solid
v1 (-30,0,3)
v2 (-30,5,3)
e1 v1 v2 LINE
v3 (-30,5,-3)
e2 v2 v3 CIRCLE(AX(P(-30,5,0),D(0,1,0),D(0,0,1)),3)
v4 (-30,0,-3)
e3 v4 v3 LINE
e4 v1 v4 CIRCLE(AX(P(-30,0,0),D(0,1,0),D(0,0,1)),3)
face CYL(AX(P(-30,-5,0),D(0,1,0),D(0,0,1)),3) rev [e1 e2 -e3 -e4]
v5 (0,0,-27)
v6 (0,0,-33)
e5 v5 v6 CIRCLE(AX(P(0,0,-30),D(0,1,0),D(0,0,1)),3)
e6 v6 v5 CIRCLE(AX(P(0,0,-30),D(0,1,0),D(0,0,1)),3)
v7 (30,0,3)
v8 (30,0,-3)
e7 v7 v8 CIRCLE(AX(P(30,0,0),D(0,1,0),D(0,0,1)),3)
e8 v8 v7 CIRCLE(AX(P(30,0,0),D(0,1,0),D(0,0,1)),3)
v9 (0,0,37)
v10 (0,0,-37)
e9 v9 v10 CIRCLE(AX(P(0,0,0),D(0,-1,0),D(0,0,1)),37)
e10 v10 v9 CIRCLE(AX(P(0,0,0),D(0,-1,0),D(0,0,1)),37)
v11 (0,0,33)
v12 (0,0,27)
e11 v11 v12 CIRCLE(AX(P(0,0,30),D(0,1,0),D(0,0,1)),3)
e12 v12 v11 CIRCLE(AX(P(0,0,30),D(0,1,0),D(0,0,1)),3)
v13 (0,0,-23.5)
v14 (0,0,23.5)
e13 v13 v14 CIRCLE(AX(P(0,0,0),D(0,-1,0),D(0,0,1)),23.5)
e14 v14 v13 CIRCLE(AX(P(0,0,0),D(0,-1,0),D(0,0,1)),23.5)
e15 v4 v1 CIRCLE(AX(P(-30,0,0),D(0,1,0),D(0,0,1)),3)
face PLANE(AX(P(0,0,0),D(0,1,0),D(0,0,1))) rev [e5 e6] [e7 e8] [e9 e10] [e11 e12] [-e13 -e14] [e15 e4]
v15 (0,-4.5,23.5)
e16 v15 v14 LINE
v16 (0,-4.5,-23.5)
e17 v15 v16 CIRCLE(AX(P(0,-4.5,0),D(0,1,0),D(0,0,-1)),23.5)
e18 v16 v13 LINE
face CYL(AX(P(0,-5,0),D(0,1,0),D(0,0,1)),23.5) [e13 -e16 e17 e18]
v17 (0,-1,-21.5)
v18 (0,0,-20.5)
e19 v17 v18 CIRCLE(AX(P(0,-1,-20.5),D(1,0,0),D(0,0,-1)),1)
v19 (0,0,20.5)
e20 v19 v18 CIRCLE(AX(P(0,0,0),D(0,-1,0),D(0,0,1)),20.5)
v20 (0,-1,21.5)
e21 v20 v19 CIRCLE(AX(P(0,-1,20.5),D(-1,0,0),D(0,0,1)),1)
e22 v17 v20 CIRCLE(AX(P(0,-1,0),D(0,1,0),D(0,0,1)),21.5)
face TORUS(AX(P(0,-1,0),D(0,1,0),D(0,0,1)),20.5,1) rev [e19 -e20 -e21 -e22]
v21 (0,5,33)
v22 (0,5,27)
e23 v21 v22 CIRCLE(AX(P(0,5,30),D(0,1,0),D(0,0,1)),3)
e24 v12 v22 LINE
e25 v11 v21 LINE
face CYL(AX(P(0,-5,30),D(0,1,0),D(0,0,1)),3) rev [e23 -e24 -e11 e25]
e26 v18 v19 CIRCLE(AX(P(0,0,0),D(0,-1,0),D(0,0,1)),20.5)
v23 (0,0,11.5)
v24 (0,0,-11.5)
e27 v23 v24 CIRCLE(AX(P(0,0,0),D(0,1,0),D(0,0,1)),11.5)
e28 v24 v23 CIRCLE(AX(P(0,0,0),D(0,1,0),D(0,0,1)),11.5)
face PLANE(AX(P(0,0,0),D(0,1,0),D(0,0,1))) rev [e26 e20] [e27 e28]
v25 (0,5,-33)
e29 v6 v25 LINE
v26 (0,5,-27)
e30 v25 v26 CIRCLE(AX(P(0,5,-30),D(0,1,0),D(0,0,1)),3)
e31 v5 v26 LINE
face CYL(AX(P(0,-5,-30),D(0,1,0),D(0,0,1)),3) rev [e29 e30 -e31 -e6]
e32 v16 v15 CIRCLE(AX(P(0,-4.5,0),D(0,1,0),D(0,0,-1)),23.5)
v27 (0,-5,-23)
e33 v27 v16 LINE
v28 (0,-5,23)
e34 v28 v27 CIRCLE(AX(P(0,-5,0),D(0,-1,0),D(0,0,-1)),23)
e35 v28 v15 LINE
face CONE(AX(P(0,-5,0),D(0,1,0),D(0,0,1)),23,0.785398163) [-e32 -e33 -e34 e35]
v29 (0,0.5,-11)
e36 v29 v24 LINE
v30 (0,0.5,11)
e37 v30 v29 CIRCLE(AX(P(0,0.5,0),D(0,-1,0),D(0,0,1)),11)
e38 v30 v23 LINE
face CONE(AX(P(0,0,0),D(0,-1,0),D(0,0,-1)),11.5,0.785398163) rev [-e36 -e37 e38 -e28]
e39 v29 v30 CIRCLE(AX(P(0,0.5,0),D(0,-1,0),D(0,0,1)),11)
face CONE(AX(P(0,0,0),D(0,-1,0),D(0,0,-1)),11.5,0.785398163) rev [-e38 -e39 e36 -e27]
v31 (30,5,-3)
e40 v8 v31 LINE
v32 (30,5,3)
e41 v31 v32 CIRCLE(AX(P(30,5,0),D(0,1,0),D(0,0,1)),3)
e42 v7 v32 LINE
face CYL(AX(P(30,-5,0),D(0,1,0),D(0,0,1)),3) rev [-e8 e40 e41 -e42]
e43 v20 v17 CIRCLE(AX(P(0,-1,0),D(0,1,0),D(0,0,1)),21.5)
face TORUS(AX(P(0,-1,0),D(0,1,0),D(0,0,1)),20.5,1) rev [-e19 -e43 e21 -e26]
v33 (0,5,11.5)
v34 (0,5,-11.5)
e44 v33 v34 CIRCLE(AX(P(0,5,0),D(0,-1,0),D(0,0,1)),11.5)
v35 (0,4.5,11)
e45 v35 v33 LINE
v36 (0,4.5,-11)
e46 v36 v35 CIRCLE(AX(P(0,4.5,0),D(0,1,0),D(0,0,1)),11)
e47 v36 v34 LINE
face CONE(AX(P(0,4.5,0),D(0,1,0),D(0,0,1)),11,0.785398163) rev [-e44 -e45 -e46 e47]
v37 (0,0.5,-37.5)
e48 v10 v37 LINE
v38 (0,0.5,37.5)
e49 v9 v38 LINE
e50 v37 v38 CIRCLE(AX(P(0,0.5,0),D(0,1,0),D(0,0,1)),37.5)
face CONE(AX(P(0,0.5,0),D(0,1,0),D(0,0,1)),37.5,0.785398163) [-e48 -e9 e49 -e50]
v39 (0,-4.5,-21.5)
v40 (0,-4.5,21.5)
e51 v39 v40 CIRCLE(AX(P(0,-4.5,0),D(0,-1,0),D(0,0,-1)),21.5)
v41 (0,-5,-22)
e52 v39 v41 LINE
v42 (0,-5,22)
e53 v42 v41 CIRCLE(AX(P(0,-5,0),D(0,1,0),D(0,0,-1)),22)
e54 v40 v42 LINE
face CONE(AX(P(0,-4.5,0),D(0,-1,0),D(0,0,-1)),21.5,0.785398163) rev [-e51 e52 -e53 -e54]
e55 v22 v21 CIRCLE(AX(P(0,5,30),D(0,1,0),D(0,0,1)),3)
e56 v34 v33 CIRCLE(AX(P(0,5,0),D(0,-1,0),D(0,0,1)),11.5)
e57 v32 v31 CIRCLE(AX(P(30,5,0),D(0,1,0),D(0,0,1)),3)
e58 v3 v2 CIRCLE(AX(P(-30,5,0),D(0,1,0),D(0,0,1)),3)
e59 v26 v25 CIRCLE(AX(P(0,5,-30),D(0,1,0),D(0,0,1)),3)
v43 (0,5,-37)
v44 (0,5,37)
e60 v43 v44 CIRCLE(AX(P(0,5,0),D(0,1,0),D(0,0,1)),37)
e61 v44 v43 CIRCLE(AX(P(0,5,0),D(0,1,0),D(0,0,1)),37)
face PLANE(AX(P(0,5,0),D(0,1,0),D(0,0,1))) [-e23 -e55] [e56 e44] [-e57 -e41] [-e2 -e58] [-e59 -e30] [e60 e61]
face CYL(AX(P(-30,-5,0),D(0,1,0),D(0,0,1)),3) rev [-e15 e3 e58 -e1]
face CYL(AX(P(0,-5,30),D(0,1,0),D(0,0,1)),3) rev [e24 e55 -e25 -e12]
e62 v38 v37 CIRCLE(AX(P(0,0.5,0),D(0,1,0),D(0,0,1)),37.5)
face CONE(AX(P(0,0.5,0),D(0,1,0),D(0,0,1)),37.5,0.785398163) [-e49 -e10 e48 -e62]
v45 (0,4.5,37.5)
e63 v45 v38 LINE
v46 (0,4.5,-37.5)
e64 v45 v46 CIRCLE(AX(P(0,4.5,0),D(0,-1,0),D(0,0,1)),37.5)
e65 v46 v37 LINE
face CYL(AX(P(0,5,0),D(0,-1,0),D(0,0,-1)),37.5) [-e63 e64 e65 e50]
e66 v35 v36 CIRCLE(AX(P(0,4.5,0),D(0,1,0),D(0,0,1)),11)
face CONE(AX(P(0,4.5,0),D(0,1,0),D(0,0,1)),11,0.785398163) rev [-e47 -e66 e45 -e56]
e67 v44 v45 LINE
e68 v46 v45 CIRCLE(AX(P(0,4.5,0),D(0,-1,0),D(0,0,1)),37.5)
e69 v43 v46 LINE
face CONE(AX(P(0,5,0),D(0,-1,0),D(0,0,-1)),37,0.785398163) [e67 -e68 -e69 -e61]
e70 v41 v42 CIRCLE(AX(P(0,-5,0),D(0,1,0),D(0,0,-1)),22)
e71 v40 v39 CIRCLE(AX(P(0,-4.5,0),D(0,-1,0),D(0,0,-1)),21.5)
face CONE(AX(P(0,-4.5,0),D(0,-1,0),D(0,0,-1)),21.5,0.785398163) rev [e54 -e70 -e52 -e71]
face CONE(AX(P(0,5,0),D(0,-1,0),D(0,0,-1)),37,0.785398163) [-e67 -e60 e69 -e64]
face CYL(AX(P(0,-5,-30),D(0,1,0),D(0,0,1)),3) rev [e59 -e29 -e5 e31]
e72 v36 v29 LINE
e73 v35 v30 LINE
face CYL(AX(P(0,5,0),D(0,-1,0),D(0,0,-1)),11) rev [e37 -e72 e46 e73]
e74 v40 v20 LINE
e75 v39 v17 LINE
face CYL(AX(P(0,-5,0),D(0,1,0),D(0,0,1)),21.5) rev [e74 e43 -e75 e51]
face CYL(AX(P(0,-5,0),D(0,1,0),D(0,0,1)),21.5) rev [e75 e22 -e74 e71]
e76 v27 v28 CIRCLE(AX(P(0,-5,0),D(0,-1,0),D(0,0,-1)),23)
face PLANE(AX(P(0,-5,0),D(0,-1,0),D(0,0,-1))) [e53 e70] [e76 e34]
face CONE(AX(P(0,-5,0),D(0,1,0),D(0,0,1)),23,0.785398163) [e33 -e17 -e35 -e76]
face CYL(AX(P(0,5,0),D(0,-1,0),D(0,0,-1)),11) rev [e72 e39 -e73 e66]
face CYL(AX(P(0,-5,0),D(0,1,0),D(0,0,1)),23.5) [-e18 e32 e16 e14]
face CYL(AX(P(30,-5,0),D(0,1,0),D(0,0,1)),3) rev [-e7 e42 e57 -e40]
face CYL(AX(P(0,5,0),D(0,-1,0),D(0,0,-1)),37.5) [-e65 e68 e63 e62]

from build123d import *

# Parameters (mm, degrees)
SKETCH_1_R          = 37.5
SKETCH_1_R_2        = 11
EXTRUDE_1_DEPTH     = 5
SKETCH_2_R          = 23.5
SKETCH_2_R_2        = 21.5
EXTRUDE_2_DEPTH     = 5
SKETCH_3_R          = 3
CUT_EXTRUDE_1_DEPTH = 54.967582862
CHAMFER_1_SIZE      = 0.5
FILLET_1_R          = 1
CHAMFER_2_SIZE      = 0.5


with BuildPart() as part:
    # 草图1 → 拉伸1 (new body)
    with BuildSketch(Plane(origin=(0, 0, 0), x_dir=(1, 0, 0), z_dir=(0, 1, 0))):
        with Locations(Location((0, 0, 0), (0, 0, 270))):
            Circle(SKETCH_1_R)
        with Locations(Location((0, 0, 0), (0, 0, 270))):
            Circle(SKETCH_1_R_2, mode=Mode.SUBTRACT)
    extrude(amount=EXTRUDE_1_DEPTH)

    # 草图2 → 拉伸2 (add)
    with BuildSketch(Plane.XZ):
        with Locations(Location((0, 0, 0), (0, 0, 90))):
            Circle(SKETCH_2_R)
        with Locations(Location((0, 0, 0), (0, 0, 270))):
            Circle(SKETCH_2_R_2, mode=Mode.SUBTRACT)
    extrude(amount=EXTRUDE_2_DEPTH)

    # 草图3 → 切除-拉伸1 (cut, through all)
    with BuildSketch(Plane(origin=(0, 5, 0), x_dir=(-1, 0, 0), z_dir=(0, 1, 0))):
        with Locations(Location((-30, 0, 0), (0, 0, 90))):
            Circle(SKETCH_3_R)
        with Locations(Location((0, 30, 0), (0, 0, 90))):
            Circle(SKETCH_3_R)
        with Locations(Location((30, 0, 0), (0, 0, 90))):
            Circle(SKETCH_3_R)
        with Locations(Location((0, -30, 0), (0, 0, 90))):
            Circle(SKETCH_3_R)
    extrude(amount=-CUT_EXTRUDE_1_DEPTH, mode=Mode.SUBTRACT)

    # 倒角1
    chamfer_1_edges = [part.edges().sort_by_distance(p)[0] for p in [
        (0, -5, -23.5),
        (0, -5, 21.5),
        (0, 0, -37.5),
        (0, 5, -37.5),
    ]]
    chamfer(chamfer_1_edges, length=CHAMFER_1_SIZE)

    # 圆角1
    fillet_1_edges = [part.edges().sort_by_distance(p)[0] for p in [
        (0, 0, 21.5),
    ]]
    fillet(fillet_1_edges, radius=FILLET_1_R)

    # 倒角2
    chamfer_2_edges = [part.edges().sort_by_distance(p)[0] for p in [
        (0, 0, -11),
        (0, 5, -11),
    ]]
    chamfer(chamfer_2_edges, length=CHAMFER_2_SIZE)


solid = part.part
